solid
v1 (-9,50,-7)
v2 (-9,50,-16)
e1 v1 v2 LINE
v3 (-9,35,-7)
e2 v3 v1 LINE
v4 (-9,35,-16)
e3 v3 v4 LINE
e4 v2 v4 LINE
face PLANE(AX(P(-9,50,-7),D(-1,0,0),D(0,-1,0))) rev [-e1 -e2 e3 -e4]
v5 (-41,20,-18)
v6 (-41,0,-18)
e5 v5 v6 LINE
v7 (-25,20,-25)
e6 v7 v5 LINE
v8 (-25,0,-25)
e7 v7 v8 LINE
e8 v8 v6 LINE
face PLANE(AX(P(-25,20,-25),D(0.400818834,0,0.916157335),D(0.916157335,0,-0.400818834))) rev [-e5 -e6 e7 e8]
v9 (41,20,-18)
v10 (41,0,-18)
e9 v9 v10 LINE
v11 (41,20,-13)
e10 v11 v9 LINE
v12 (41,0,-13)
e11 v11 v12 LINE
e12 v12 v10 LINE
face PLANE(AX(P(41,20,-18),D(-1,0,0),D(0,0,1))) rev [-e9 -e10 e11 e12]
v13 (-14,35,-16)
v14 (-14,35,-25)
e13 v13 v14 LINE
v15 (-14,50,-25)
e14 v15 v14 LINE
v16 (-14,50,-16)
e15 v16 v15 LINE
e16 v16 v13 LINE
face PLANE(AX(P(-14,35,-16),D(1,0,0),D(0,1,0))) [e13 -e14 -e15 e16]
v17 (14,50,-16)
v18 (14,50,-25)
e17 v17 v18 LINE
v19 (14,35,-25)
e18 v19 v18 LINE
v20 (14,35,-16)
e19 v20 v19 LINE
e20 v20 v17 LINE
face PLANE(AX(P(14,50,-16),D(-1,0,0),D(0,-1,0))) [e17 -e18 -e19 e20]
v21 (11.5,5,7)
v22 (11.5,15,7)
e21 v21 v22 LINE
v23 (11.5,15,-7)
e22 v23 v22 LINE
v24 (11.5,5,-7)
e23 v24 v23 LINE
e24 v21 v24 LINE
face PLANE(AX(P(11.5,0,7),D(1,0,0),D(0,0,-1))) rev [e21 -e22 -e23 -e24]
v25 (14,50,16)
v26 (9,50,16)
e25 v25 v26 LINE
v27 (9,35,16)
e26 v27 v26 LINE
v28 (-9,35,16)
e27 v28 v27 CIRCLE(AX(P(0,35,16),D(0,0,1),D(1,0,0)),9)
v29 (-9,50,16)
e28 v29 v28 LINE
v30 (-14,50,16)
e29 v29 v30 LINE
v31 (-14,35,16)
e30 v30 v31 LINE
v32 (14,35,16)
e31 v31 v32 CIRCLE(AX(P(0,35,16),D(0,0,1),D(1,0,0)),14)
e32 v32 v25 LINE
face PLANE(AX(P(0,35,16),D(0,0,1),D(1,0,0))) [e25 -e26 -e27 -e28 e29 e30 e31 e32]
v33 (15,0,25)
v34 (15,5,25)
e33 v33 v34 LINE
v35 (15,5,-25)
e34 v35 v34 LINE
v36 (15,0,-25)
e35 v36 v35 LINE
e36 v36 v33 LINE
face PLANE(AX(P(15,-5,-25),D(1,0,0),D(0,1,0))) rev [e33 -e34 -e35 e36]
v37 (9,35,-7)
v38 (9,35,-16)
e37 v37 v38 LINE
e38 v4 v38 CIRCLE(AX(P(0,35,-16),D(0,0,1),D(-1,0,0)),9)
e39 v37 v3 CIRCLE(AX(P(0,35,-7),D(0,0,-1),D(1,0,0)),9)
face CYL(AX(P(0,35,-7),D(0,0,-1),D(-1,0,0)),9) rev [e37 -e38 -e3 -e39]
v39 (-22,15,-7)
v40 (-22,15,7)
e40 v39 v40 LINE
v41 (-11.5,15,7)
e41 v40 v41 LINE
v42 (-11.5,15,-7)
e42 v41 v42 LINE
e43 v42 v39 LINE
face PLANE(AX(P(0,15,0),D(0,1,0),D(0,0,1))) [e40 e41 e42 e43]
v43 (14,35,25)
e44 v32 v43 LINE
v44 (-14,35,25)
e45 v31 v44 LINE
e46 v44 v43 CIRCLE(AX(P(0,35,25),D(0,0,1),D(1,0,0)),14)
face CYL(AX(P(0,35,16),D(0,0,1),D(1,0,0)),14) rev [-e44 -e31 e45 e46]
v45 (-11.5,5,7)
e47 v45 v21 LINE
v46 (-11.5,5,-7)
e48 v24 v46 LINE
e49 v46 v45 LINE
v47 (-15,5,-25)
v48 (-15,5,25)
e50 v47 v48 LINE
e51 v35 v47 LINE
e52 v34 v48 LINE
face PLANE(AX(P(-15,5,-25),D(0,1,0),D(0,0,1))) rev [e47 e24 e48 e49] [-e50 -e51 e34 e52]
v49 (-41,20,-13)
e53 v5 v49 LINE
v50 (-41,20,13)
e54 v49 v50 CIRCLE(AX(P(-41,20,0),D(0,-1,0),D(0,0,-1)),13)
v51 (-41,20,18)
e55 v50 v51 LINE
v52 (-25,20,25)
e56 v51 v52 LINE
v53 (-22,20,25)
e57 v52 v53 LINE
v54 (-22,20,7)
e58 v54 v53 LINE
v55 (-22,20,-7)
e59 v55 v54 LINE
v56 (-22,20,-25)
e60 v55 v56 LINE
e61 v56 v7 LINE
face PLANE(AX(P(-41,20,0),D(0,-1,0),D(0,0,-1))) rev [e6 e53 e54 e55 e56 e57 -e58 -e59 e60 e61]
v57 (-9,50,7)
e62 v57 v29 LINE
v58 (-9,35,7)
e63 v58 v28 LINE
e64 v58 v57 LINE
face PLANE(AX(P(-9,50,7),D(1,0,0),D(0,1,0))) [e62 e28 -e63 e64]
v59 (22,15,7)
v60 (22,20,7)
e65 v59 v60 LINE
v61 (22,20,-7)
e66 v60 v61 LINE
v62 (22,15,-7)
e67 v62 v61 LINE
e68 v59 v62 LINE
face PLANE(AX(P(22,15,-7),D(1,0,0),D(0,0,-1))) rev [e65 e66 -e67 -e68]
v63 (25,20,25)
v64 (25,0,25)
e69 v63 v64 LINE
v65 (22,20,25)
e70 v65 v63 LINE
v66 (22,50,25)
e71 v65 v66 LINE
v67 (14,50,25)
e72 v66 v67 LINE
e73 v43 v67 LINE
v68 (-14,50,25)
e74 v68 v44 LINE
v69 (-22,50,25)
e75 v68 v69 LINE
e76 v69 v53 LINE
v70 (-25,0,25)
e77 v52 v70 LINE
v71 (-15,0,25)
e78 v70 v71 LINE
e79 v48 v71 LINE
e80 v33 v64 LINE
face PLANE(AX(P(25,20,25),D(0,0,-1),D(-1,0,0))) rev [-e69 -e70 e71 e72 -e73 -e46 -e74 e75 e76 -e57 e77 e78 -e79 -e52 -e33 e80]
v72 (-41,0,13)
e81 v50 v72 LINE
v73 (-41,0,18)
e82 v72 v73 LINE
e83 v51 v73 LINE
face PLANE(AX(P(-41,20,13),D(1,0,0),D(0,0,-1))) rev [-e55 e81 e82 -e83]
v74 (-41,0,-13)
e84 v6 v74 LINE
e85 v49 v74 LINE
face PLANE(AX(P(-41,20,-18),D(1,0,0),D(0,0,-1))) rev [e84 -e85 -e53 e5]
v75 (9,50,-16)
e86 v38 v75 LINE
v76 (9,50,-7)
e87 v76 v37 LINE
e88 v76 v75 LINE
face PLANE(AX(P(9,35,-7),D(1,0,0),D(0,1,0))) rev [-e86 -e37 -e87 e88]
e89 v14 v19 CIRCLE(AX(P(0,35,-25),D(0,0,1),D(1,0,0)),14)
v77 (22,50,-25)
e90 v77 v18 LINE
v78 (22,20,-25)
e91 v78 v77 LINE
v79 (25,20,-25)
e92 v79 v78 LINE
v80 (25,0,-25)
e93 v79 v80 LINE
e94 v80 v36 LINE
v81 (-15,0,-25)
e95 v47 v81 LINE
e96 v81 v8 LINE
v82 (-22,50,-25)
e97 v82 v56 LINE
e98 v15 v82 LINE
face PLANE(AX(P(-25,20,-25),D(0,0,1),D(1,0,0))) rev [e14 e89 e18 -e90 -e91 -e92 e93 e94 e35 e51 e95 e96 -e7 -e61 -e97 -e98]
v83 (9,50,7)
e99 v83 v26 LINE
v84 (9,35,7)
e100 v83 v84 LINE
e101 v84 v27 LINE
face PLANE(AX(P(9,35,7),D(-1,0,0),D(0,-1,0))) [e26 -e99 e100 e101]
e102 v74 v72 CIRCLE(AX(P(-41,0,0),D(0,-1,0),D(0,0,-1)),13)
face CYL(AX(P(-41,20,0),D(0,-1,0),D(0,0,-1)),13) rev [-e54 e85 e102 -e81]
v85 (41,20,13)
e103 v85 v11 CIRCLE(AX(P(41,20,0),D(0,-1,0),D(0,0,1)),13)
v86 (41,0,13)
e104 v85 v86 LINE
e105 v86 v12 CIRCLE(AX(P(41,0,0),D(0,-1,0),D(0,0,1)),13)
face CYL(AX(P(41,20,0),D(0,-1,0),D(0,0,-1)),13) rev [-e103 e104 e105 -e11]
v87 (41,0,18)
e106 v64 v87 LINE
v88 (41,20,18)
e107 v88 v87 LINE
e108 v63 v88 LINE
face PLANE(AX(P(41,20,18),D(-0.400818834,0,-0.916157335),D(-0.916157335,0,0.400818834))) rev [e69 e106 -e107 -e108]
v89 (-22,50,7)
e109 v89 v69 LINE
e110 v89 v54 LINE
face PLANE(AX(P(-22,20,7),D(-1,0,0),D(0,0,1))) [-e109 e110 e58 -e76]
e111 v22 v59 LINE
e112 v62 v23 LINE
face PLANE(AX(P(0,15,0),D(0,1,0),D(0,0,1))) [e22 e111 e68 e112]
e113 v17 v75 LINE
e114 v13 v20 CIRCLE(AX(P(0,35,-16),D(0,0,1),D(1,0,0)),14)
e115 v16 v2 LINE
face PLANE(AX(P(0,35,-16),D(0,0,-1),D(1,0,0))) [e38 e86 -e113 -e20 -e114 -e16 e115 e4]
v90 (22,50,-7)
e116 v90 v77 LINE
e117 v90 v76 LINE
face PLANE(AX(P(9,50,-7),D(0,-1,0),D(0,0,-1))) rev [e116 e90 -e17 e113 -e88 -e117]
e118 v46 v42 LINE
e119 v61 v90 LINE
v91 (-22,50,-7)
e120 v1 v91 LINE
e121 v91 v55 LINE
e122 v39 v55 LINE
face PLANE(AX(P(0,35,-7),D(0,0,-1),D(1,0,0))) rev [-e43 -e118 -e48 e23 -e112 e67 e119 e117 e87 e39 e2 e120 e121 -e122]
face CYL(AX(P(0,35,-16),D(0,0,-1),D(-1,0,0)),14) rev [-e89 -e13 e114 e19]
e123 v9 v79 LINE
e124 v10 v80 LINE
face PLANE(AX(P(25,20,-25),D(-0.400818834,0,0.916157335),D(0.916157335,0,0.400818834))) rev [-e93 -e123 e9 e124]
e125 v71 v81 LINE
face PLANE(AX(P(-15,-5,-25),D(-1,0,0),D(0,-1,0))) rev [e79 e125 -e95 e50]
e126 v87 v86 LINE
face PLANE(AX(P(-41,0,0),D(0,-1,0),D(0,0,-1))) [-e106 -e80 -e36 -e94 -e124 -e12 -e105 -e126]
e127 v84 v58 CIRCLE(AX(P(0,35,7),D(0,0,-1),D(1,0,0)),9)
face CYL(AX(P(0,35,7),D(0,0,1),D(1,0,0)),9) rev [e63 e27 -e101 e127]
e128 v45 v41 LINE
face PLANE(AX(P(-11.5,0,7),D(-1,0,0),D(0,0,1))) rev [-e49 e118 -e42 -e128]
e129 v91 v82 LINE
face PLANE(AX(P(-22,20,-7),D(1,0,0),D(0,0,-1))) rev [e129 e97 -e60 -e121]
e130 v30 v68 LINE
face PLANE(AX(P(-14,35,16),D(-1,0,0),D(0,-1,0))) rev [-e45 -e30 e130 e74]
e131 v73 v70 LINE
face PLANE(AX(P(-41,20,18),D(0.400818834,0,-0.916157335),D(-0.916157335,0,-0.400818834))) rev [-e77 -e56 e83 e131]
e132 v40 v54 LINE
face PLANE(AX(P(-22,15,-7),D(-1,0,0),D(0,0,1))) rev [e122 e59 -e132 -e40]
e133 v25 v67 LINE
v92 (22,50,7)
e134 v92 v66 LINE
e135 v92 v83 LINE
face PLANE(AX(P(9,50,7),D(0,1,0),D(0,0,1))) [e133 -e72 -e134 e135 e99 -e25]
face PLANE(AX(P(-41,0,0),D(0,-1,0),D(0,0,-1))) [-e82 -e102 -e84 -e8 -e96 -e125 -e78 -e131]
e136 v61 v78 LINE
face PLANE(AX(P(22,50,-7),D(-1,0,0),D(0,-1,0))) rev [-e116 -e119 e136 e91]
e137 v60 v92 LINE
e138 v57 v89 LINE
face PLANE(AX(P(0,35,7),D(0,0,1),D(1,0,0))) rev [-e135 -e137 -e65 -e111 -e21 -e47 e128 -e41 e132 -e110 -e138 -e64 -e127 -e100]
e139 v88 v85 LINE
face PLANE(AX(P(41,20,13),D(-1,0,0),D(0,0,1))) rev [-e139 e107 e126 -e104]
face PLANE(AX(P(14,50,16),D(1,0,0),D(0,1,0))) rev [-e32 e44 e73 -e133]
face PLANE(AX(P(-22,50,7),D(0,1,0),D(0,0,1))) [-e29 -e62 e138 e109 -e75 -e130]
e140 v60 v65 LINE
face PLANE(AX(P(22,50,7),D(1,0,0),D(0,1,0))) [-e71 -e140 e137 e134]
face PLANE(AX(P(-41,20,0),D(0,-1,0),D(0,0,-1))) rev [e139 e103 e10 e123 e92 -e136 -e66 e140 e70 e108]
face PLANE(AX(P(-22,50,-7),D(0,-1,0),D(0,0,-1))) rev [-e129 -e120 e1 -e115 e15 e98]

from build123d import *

# Parameters (mm, degrees)
BASE_BLOCK_DEPTH         = 20
UPRIGHTS_DEPTH           = 18
UPRIGHT_NOTCH_DEPTH      = 9
UNDERSIDE_SLOT_PROFILE_W = 30
UNDERSIDE_SLOT_PROFILE_H = 10
UNDERSIDE_SLOT_DEPTH     = 82.737384348
SADDLE_CUT_PROFILE_W     = 23
SADDLE_CUT_PROFILE_H     = 14
SADDLE_CUT_DEPTH         = 57.621550668
UPRIGHT_SLOT_PROFILE_W   = 44
UPRIGHT_SLOT_PROFILE_H   = 14
UPRIGHT_SLOT_CUT_DEPTH   = 5


with BuildPart() as part:
    # Base Block Profile → Base Block (new body)
    with BuildSketch(Plane(origin=(0, 0, 0), x_dir=(1, 0, 0), z_dir=(0, 1, 0))):
        with BuildLine():
            Line((-25, 25), (25, 25))
            Line((25, 25), (41, 18))
            Line((41, 18), (41, 13))
            ThreePointArc((41, 13), (28, 0), (41, -13))
            Line((41, -13), (41, -18))
            Line((41, -18), (25, -25))
            Line((25, -25), (-25, -25))
            Line((-25, -25), (-41, -18))
            Line((-41, -18), (-41, -13))
            ThreePointArc((-41, -13), (-28, 0), (-41, 13))
            Line((-41, 13), (-41, 18))
            Line((-41, 18), (-25, 25))
        make_face()
    extrude(amount=BASE_BLOCK_DEPTH)

    # Uprights Profile → Uprights (add)
    with BuildSketch(Plane.XY.offset(25)):
        with BuildLine():
            Line((-22, 20), (-22, 50))
            Line((-22, 50), (-9, 50))
            Line((-9, 50), (-9, 35))
            ThreePointArc((-9, 35), (0, 26), (9, 35))
            Line((9, 35), (9, 50))
            Line((9, 50), (22, 50))
            Line((22, 50), (22, 20))
            Line((22, 20), (-22, 20))
        make_face()
    uprights = extrude(amount=-UPRIGHTS_DEPTH)

    # Upright Notch Profile → Upright Notch (cut)
    with BuildSketch(Plane.XY.offset(25)):
        with BuildLine():
            Line((-14, 50), (14, 50))
            Line((14, 50), (14, 35))
            ThreePointArc((14, 35), (0, 21), (-14, 35))
            Line((-14, 35), (-14, 50))
        make_face()
    upright_notch = extrude(amount=-UPRIGHT_NOTCH_DEPTH, mode=Mode.SUBTRACT)

    # Upright Notch Mirror: Uprights, Upright Notch across plane
    add(uprights.mirror(Plane.XY))
    add(upright_notch.mirror(Plane.XY), mode=Mode.SUBTRACT)

    # Underside Slot Profile → Underside Slot (cut, through all)
    with BuildSketch(Plane.XY.offset(25)):
        Rectangle(UNDERSIDE_SLOT_PROFILE_W, UNDERSIDE_SLOT_PROFILE_H)
    extrude(amount=-UNDERSIDE_SLOT_DEPTH, mode=Mode.SUBTRACT)

    # Saddle Cut Profile → Saddle Cut (cut, through all)
    with BuildSketch(Plane(origin=(0, 20, 0), x_dir=(1, 0, 0), z_dir=(0, 1, 0))):
        Rectangle(SADDLE_CUT_PROFILE_W, SADDLE_CUT_PROFILE_H)
    extrude(amount=-SADDLE_CUT_DEPTH, mode=Mode.SUBTRACT)

    # Upright Slot Profile → Upright Slot Cut (cut)
    with BuildSketch(Plane(origin=(0, 20, 0), x_dir=(1, 0, 0), z_dir=(0, 1, 0))):
        Rectangle(UPRIGHT_SLOT_PROFILE_W, UPRIGHT_SLOT_PROFILE_H)
    extrude(amount=-UPRIGHT_SLOT_CUT_DEPTH, mode=Mode.SUBTRACT)


solid = part.part
